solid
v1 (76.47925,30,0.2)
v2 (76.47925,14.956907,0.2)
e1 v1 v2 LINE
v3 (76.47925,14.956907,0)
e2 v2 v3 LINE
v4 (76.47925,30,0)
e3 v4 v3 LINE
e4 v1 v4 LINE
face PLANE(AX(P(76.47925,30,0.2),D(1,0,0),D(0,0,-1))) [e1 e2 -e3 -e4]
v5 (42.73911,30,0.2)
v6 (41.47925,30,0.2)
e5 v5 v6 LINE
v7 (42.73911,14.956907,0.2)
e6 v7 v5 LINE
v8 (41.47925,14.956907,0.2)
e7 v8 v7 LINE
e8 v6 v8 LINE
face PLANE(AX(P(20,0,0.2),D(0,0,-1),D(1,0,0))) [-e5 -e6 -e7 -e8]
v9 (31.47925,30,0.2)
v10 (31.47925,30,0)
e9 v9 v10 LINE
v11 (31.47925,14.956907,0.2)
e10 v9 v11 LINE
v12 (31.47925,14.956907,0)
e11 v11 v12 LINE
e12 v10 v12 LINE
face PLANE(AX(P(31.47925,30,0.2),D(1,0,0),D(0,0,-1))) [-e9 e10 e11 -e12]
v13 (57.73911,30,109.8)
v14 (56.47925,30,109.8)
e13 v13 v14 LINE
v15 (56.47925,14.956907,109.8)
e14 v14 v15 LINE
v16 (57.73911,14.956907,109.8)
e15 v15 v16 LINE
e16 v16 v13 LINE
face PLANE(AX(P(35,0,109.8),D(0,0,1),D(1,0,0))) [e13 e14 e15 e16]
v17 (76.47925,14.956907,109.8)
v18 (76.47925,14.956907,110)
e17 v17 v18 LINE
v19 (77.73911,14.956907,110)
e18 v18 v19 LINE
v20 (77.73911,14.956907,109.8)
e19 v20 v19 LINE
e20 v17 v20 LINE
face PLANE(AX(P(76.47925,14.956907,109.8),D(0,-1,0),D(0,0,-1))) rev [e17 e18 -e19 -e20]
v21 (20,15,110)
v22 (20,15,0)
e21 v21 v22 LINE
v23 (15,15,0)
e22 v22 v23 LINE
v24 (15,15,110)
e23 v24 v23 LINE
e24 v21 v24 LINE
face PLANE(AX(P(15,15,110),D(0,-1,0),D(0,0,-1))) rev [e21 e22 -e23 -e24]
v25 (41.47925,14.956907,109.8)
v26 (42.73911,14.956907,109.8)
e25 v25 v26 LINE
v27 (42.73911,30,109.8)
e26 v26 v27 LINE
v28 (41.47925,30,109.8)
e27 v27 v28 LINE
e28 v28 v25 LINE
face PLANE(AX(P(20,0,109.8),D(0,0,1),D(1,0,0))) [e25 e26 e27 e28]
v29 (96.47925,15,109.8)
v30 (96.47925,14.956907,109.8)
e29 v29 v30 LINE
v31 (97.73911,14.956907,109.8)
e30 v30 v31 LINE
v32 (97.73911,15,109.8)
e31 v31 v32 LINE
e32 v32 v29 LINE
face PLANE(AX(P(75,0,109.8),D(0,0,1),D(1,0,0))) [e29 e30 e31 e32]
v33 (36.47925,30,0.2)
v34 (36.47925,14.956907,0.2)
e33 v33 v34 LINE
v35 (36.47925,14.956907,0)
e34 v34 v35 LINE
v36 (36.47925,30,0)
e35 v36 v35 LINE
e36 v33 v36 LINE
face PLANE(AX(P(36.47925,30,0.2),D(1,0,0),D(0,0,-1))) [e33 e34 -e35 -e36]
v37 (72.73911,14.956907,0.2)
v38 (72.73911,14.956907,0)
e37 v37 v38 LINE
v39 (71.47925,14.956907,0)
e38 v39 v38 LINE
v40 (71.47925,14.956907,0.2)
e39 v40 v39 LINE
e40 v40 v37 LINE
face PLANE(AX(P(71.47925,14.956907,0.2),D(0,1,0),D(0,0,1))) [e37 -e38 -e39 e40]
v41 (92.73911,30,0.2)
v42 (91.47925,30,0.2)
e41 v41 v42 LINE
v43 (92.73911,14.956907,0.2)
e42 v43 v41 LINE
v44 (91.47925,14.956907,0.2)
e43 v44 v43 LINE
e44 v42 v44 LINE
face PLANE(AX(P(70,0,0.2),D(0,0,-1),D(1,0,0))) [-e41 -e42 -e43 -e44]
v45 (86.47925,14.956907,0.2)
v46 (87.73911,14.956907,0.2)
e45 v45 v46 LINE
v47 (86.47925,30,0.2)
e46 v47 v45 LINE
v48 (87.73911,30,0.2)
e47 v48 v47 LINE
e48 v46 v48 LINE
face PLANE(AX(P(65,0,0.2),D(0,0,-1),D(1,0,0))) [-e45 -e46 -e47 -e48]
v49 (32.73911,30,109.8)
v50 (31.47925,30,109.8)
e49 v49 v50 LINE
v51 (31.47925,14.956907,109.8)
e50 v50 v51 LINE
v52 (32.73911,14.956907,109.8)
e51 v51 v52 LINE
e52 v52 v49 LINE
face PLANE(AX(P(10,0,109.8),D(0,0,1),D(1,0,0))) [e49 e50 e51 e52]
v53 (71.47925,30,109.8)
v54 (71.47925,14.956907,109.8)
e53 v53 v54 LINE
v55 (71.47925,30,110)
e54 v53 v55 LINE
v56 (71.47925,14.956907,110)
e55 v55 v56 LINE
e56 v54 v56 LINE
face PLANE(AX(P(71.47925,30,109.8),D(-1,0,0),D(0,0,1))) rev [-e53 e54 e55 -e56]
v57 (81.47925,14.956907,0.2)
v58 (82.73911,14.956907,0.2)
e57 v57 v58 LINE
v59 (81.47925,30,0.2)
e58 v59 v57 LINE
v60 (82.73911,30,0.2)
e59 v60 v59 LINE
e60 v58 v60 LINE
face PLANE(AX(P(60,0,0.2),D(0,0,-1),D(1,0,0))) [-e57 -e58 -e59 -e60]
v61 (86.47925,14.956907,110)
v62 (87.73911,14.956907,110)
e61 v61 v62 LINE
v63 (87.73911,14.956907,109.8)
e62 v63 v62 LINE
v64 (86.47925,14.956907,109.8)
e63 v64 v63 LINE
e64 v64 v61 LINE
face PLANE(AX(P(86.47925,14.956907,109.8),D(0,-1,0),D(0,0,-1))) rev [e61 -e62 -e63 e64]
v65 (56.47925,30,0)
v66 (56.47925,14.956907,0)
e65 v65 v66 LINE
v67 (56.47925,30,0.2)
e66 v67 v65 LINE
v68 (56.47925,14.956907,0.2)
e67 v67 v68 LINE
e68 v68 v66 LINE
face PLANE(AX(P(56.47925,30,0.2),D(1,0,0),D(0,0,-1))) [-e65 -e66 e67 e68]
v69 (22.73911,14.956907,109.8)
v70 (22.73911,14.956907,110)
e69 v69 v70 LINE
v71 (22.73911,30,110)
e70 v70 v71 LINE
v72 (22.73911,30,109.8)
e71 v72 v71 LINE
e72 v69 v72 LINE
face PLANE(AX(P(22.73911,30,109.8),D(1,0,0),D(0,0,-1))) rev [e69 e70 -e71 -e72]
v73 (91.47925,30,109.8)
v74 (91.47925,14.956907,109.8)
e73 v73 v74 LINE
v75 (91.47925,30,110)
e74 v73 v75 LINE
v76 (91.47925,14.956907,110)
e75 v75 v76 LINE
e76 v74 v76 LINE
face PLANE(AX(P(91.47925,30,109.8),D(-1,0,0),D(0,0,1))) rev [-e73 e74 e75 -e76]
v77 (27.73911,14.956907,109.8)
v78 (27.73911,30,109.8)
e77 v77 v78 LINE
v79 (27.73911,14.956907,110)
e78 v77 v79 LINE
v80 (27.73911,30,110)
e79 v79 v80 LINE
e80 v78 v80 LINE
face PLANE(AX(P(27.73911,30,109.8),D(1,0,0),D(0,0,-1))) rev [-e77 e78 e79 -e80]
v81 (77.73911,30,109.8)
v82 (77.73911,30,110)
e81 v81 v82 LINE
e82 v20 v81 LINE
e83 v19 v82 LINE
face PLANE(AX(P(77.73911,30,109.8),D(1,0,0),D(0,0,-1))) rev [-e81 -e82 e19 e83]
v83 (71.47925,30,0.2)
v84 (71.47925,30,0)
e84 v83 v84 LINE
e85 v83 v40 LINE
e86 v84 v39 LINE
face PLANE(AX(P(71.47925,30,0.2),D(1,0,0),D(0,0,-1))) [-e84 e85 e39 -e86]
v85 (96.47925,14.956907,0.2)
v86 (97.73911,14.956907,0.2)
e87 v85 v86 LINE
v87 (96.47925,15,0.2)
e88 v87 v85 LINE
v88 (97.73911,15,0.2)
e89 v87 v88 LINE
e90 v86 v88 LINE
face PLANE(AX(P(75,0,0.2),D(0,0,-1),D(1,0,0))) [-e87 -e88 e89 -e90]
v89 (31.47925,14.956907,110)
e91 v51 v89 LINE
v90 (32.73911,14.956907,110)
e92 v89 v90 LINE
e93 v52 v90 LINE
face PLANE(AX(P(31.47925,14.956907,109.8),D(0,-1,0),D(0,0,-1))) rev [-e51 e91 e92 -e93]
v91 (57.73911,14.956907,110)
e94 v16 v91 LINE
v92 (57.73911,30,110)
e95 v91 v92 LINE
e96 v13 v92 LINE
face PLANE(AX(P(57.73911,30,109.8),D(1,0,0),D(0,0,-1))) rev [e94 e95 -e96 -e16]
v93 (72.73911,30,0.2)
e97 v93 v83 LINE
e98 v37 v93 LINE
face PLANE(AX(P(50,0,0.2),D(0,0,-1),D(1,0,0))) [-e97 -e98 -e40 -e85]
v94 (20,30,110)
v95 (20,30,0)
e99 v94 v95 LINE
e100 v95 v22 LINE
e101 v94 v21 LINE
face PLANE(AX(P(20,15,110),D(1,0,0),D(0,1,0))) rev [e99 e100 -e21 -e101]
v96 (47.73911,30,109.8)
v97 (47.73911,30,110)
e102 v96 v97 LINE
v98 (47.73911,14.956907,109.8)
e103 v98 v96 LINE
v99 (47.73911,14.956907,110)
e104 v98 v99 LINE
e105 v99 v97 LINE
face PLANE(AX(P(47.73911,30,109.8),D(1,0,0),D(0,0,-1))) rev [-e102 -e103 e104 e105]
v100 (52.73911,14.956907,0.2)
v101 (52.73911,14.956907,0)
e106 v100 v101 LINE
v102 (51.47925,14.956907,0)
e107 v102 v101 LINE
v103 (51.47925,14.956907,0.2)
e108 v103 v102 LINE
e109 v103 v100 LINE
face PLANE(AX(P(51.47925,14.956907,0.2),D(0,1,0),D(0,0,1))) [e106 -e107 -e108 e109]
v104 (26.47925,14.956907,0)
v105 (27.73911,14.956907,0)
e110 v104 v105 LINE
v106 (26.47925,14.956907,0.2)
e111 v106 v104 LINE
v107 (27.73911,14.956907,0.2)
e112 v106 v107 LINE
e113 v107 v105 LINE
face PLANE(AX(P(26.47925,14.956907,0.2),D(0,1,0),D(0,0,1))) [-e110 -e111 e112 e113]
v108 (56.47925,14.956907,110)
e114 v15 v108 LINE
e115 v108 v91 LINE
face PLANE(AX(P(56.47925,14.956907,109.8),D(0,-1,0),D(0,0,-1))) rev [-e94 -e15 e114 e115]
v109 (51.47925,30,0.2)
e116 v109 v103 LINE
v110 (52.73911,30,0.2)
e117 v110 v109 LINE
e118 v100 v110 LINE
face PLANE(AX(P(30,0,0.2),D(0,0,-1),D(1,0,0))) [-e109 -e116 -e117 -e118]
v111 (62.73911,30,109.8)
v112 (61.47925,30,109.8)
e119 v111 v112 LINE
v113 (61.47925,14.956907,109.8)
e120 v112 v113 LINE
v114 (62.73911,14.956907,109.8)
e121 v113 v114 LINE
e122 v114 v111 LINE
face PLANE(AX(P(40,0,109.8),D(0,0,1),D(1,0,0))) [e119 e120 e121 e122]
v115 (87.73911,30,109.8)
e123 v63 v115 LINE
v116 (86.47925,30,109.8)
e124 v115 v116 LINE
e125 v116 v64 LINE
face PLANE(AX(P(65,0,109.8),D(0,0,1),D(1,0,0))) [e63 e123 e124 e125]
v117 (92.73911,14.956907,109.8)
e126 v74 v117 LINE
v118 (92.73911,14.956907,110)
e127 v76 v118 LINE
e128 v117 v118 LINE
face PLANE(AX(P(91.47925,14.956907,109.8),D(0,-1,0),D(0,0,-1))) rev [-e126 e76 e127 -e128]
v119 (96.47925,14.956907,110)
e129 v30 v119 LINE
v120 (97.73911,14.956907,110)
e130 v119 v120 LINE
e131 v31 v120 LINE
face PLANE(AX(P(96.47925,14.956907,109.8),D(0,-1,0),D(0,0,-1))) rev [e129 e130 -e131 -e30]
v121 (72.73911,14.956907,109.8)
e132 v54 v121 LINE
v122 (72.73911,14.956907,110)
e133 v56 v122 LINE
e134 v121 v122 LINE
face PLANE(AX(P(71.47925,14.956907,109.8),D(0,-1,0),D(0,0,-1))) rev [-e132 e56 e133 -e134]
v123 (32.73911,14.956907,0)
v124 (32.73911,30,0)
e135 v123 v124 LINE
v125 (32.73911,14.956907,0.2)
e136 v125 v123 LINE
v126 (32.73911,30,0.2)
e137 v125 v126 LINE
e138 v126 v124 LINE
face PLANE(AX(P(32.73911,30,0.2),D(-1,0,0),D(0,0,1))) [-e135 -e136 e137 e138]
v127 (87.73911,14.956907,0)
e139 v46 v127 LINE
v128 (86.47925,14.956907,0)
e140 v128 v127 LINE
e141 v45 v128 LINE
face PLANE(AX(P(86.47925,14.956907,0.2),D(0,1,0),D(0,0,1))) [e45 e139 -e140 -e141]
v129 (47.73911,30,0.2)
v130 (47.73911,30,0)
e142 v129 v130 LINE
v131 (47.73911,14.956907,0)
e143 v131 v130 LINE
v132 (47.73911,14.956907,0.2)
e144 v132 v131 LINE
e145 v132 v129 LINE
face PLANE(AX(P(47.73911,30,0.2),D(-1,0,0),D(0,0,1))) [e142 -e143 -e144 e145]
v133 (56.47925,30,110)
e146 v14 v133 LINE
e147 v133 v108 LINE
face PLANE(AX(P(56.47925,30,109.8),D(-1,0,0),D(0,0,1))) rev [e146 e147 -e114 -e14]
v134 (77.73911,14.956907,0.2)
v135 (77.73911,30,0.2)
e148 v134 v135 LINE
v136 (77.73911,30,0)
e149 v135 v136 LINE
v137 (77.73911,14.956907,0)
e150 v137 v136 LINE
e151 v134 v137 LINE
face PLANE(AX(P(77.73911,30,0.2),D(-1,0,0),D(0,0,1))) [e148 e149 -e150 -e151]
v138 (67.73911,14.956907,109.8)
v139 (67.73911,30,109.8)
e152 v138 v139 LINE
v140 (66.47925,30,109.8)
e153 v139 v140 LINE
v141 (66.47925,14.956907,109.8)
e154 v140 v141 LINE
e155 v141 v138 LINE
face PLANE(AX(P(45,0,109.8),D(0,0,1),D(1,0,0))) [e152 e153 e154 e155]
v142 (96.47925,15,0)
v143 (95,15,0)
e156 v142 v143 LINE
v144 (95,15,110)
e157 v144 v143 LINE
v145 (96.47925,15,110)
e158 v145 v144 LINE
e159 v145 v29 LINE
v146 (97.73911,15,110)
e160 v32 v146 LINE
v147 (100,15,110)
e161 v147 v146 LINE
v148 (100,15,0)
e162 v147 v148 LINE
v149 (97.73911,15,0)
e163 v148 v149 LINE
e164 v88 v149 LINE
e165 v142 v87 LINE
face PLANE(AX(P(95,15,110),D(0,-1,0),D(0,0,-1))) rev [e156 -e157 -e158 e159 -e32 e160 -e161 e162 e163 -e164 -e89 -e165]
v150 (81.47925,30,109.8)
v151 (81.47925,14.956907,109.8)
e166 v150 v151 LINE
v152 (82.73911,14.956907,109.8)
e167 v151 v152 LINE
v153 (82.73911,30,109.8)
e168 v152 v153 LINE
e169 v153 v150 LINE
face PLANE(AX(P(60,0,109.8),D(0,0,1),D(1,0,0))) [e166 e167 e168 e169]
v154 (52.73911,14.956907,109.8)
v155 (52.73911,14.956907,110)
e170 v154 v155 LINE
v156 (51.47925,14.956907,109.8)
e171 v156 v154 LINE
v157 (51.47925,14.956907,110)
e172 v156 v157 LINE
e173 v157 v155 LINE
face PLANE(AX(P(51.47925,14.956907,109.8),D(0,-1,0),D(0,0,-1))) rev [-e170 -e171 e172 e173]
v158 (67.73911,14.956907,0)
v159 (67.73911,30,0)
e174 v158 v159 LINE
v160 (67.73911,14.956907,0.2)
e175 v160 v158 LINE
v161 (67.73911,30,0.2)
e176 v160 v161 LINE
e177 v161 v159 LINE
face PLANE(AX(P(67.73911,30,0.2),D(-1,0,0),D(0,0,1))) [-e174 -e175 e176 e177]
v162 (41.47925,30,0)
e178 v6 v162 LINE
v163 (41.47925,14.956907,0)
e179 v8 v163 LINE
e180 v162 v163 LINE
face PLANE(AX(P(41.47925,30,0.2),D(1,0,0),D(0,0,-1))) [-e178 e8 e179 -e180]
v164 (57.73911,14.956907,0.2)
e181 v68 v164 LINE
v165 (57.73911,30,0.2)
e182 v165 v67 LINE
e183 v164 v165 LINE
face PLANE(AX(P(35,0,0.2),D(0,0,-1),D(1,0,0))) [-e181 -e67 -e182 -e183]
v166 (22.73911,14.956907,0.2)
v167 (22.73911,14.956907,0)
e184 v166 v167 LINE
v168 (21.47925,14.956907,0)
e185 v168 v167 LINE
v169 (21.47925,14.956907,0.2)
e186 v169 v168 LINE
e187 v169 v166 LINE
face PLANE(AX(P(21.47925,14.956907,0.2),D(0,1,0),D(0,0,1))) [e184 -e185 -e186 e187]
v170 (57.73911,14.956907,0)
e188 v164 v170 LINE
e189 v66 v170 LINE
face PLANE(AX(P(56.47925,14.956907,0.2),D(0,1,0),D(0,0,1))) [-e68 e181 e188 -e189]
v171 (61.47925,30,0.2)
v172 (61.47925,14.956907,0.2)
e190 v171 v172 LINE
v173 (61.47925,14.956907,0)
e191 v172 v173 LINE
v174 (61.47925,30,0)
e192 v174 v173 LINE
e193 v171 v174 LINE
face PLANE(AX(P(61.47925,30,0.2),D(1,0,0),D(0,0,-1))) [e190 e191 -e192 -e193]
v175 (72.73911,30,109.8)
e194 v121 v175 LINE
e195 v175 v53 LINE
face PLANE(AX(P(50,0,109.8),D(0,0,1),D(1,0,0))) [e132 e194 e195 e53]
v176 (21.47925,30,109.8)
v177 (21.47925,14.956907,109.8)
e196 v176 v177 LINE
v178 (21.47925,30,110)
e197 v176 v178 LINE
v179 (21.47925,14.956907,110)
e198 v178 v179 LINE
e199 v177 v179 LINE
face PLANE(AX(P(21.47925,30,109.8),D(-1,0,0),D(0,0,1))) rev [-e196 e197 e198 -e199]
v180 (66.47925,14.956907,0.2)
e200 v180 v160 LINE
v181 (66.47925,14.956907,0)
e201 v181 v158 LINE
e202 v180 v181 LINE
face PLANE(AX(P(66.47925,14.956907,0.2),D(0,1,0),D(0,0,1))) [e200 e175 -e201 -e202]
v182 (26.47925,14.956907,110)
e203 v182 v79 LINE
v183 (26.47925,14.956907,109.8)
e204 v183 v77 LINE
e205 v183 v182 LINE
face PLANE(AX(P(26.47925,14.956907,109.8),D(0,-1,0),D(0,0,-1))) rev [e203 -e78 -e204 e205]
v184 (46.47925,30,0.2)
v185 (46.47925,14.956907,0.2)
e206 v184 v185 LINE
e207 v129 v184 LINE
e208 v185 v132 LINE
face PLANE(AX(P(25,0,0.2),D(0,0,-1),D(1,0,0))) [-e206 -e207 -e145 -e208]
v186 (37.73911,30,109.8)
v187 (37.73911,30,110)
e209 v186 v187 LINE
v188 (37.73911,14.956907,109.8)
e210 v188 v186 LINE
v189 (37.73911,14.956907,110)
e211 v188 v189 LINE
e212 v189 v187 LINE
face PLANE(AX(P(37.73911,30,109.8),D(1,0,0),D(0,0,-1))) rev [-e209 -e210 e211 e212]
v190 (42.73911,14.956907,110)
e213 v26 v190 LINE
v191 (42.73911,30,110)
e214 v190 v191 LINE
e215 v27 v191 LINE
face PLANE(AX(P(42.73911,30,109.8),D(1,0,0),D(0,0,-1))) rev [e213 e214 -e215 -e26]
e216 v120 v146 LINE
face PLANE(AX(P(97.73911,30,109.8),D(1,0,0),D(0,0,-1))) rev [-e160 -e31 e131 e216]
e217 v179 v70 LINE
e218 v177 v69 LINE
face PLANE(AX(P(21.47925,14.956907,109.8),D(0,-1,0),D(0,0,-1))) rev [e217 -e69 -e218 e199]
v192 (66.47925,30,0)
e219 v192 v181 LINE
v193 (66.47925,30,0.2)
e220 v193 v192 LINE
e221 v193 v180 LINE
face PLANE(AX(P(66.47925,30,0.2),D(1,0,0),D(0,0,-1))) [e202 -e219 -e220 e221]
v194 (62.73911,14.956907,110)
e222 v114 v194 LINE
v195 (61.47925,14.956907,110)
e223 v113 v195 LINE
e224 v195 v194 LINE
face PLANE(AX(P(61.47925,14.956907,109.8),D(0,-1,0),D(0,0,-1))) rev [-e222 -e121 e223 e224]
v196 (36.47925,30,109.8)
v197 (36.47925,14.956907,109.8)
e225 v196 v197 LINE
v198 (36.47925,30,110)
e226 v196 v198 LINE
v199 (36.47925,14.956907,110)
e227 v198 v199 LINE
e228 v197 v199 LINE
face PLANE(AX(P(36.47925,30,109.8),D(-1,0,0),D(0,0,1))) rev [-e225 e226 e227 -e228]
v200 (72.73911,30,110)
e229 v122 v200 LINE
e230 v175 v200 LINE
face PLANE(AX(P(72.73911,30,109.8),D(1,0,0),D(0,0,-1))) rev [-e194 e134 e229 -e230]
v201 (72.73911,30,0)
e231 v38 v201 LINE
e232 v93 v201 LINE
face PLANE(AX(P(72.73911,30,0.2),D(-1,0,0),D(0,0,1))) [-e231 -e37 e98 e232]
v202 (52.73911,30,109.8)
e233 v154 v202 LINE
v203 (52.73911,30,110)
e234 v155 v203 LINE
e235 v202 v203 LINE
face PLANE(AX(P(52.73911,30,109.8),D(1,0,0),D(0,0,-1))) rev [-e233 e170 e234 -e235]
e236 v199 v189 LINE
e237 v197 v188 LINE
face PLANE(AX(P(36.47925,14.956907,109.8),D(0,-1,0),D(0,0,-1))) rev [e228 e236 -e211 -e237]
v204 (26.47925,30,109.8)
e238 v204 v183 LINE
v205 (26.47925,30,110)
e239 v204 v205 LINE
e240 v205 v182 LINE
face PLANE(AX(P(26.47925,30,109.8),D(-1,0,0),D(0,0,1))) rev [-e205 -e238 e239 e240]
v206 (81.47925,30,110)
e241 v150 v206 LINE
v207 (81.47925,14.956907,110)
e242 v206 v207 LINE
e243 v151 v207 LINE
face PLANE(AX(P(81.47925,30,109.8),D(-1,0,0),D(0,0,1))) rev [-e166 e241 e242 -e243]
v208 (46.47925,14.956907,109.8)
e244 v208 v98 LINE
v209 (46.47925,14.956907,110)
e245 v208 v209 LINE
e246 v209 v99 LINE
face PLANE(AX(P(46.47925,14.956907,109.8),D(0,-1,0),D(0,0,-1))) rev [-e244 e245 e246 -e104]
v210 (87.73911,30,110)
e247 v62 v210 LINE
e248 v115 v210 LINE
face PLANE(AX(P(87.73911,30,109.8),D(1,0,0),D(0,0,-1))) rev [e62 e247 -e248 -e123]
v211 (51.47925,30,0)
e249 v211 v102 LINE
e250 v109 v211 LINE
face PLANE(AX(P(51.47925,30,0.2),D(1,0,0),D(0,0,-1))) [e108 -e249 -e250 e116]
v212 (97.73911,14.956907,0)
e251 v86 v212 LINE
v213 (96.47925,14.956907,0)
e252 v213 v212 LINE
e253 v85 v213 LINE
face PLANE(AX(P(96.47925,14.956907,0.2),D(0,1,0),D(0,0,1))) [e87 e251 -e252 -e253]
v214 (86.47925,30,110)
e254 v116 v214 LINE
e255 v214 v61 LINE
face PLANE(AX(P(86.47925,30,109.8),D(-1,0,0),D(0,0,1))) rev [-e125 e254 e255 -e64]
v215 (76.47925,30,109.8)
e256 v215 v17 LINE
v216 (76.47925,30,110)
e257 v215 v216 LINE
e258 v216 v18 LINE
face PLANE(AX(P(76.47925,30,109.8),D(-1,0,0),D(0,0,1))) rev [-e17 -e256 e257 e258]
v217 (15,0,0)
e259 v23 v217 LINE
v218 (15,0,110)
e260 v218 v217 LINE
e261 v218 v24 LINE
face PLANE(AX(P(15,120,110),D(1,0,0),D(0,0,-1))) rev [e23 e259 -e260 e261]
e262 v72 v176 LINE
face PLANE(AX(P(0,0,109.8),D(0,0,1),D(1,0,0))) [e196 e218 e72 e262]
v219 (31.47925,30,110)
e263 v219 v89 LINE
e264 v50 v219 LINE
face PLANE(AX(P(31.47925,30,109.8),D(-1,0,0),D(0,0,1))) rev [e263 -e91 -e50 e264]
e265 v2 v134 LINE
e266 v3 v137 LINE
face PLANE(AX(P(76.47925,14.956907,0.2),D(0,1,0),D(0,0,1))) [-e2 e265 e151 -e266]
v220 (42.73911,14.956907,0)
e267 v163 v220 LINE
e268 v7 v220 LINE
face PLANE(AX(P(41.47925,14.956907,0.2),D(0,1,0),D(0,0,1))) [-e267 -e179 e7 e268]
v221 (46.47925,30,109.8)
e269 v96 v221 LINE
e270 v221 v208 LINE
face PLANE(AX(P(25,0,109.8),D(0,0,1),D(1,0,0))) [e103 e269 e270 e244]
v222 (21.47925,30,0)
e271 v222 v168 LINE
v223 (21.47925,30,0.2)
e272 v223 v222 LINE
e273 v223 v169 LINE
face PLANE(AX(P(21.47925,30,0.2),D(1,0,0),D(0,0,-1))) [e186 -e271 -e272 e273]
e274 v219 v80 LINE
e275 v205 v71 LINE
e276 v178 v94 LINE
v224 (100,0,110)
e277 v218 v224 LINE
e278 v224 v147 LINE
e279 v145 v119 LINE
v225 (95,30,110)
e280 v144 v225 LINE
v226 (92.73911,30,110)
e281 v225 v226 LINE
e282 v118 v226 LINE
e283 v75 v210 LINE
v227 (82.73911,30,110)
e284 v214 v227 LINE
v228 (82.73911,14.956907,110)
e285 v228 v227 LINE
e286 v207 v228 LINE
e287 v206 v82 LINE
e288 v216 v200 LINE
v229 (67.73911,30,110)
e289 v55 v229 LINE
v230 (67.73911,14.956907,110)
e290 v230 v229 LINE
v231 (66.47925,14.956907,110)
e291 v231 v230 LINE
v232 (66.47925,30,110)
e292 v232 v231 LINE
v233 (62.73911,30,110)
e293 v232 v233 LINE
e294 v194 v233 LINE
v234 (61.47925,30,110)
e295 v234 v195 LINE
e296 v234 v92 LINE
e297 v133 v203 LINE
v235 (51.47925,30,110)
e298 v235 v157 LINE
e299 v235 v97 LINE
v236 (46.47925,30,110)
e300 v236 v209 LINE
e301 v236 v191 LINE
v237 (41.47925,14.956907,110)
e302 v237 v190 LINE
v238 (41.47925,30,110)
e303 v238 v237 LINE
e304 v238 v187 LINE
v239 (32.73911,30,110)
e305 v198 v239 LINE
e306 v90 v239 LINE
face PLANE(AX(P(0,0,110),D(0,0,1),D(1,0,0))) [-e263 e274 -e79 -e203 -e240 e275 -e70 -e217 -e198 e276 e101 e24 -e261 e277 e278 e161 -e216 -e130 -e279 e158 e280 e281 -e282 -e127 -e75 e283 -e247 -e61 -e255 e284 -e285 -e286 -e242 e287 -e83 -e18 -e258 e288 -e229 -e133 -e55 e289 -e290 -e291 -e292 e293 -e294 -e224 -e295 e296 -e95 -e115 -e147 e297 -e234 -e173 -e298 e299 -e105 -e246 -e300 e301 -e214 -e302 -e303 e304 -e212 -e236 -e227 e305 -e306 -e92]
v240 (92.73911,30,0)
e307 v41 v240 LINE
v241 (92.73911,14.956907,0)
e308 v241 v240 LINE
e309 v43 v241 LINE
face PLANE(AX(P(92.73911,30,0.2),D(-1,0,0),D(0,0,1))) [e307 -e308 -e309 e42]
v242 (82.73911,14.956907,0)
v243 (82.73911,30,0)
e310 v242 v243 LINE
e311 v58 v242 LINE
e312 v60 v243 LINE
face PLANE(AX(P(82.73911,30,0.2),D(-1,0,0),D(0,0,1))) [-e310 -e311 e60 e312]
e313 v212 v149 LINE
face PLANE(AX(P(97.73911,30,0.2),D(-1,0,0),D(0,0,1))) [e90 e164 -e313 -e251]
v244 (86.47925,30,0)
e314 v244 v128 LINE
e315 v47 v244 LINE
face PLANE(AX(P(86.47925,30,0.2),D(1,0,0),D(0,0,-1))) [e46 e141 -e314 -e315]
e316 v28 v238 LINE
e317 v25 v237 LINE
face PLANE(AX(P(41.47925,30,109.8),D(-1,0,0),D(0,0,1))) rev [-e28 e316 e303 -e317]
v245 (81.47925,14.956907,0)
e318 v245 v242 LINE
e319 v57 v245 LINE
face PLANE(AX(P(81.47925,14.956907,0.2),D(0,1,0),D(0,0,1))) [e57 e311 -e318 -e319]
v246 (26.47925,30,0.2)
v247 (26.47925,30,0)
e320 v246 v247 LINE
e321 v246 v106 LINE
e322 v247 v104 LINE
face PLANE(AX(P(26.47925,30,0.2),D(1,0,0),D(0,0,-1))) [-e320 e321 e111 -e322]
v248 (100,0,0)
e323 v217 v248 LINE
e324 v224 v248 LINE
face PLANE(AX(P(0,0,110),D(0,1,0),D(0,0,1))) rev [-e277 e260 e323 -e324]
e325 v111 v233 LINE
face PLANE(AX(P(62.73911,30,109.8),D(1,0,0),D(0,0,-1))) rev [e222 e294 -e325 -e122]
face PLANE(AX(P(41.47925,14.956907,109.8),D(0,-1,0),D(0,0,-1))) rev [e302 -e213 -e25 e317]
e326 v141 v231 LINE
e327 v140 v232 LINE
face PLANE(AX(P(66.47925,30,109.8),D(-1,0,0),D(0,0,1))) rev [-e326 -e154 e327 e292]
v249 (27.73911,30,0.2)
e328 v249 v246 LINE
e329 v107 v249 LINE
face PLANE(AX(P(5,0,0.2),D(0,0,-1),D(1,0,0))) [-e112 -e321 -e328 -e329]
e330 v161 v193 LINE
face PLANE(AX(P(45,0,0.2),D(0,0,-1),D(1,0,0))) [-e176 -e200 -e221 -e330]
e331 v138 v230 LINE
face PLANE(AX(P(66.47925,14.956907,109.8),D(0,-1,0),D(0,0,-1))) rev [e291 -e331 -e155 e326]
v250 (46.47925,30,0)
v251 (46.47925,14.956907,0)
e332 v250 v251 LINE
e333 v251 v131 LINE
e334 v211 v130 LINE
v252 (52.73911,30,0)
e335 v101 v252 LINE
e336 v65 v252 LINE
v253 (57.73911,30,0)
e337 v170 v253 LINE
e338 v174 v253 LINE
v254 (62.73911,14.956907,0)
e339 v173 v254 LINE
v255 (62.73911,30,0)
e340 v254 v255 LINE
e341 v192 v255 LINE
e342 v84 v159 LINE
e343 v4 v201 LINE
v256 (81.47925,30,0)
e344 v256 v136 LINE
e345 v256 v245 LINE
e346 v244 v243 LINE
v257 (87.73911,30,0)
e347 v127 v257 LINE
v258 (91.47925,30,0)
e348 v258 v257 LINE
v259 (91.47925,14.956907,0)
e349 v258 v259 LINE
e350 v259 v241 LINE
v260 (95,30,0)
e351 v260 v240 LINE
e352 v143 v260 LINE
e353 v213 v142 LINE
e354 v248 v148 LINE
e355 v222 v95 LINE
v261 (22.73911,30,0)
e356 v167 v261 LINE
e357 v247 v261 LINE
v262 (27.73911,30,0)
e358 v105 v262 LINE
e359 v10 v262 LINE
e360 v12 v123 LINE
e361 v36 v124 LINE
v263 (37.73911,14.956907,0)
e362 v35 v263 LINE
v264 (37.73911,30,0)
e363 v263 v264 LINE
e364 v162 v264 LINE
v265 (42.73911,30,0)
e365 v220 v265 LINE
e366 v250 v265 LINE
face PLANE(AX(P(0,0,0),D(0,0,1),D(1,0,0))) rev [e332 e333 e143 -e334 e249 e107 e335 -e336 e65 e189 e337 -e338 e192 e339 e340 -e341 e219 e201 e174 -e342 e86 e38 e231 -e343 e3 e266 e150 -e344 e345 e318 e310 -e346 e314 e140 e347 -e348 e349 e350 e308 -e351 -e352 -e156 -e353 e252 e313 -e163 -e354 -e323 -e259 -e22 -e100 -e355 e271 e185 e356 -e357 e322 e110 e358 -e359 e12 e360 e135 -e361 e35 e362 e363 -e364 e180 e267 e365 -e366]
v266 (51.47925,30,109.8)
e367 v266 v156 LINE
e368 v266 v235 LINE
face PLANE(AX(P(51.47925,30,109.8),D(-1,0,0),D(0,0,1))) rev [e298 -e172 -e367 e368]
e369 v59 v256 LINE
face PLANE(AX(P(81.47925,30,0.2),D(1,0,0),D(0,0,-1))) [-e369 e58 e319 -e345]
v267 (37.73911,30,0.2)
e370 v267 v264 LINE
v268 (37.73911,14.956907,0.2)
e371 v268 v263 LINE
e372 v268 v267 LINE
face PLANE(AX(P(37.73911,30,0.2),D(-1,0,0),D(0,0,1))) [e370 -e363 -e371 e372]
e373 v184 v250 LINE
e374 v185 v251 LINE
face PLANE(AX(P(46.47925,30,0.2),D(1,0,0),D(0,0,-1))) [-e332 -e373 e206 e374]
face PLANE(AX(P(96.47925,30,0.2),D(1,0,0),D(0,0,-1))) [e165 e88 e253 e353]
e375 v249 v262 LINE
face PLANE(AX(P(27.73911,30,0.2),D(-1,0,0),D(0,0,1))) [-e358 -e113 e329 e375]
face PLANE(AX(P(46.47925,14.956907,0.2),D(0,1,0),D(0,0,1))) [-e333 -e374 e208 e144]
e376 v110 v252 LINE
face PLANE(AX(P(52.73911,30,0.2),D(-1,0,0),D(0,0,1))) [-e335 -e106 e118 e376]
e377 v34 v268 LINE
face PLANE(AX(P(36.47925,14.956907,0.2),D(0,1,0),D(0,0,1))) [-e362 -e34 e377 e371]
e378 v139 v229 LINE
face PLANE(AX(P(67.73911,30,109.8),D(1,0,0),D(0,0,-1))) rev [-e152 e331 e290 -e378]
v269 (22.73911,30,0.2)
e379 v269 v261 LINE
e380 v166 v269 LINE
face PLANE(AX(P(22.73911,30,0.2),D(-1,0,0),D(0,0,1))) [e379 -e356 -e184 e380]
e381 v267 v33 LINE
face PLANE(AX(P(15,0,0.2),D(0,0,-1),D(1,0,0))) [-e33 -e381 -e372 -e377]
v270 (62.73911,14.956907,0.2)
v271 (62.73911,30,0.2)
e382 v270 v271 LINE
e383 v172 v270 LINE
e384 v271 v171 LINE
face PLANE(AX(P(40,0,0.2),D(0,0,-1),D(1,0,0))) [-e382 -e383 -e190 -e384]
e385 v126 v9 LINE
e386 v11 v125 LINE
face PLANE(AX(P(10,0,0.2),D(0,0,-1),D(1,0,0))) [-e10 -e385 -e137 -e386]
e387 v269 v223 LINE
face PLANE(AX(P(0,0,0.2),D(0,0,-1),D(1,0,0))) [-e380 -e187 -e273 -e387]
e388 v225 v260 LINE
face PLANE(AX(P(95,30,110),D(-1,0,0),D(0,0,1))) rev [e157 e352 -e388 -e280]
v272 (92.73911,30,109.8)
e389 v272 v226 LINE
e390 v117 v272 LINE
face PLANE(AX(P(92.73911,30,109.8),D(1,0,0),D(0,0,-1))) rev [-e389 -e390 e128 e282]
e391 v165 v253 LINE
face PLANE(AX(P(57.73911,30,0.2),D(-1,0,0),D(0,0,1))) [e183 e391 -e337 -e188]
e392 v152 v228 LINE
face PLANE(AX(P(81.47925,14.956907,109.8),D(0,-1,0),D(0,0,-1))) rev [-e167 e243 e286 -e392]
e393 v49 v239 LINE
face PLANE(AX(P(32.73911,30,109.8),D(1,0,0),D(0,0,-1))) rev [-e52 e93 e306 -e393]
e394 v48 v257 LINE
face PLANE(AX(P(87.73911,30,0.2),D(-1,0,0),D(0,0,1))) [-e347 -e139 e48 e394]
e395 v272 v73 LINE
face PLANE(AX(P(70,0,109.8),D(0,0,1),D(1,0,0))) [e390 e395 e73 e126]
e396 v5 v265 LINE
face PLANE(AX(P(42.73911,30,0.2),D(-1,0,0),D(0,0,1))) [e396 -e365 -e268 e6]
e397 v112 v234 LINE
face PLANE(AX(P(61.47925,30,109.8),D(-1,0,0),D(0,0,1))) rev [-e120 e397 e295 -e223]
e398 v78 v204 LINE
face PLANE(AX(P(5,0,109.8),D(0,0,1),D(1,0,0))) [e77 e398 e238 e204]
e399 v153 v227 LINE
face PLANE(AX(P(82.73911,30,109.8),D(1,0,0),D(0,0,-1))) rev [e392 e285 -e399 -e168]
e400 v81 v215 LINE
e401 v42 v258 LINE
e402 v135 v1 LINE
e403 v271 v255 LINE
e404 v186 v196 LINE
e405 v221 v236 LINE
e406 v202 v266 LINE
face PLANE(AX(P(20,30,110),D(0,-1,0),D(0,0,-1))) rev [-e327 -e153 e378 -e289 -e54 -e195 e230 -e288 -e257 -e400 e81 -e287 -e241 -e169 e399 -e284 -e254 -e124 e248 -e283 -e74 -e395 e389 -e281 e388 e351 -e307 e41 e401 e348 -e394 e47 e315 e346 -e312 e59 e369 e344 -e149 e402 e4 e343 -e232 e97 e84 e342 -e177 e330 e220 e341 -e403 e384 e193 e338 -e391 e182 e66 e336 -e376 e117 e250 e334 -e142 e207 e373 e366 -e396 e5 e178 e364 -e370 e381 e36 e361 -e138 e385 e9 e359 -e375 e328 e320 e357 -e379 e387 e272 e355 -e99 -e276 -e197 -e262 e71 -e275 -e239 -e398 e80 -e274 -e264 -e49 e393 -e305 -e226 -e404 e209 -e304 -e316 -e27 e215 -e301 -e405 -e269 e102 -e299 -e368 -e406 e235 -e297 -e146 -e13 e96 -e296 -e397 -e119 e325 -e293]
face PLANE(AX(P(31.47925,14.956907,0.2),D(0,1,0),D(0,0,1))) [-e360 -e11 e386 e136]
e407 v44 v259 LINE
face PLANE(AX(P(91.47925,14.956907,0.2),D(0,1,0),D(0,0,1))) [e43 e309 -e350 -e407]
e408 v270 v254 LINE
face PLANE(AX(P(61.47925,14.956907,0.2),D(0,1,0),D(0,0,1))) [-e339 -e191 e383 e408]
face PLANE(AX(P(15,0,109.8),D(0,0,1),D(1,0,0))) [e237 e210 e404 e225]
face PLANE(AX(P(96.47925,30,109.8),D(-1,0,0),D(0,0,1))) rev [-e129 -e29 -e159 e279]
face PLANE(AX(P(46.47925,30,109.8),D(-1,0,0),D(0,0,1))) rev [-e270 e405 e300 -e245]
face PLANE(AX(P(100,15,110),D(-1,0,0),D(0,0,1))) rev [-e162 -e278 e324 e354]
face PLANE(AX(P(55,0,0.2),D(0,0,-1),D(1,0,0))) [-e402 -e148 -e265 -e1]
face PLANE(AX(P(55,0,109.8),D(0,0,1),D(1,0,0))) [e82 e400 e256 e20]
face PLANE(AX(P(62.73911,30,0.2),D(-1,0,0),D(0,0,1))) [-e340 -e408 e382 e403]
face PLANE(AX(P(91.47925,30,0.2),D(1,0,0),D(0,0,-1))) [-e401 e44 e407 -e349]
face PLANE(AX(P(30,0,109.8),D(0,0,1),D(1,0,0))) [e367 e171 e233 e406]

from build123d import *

# Parameters (mm, degrees)
BOSS_EXTRUDE1_DEPTH      = 110
SKETCH2_W                = 1.259860676
SKETCH2_H                = 15.043092937
CUT_EXTRUDE1_DEPTH       = 0.2
LPATTERN1_COUNT          = 16
LPATTERN1_PITCH          = 5
MIRROR1_COPY_1_SKETCH_W  = 1.259860676
MIRROR1_COPY_1_SKETCH_H  = 15.043092937
MIRROR1_COPY_1_DEPTH     = 0.2
MIRROR1_COPY_2_SKETCH_W  = 1.259860676
MIRROR1_COPY_2_SKETCH_H  = 15.043092937
MIRROR1_COPY_2_DEPTH     = 0.2
MIRROR1_COPY_3_SKETCH_W  = 1.259860676
MIRROR1_COPY_3_SKETCH_H  = 15.043092937
MIRROR1_COPY_3_DEPTH     = 0.2
MIRROR1_COPY_4_SKETCH_W  = 1.259860676
MIRROR1_COPY_4_SKETCH_H  = 15.043092937
MIRROR1_COPY_4_DEPTH     = 0.2
MIRROR1_COPY_5_SKETCH_W  = 1.259860676
MIRROR1_COPY_5_SKETCH_H  = 15.043092937
MIRROR1_COPY_5_DEPTH     = 0.2
MIRROR1_COPY_6_SKETCH_W  = 1.259860676
MIRROR1_COPY_6_SKETCH_H  = 15.043092937
MIRROR1_COPY_6_DEPTH     = 0.2
MIRROR1_COPY_7_SKETCH_W  = 1.259860676
MIRROR1_COPY_7_SKETCH_H  = 15.043092937
MIRROR1_COPY_7_DEPTH     = 0.2
MIRROR1_COPY_8_SKETCH_W  = 1.259860676
MIRROR1_COPY_8_SKETCH_H  = 15.043092937
MIRROR1_COPY_8_DEPTH     = 0.2
MIRROR1_COPY_9_SKETCH_W  = 1.259860676
MIRROR1_COPY_9_SKETCH_H  = 15.043092937
MIRROR1_COPY_9_DEPTH     = 0.2
MIRROR1_COPY_10_SKETCH_W = 1.259860676
MIRROR1_COPY_10_SKETCH_H = 15.043092937
MIRROR1_COPY_10_DEPTH    = 0.2
MIRROR1_COPY_11_SKETCH_W = 1.259860676
MIRROR1_COPY_11_SKETCH_H = 15.043092937
MIRROR1_COPY_11_DEPTH    = 0.2
MIRROR1_COPY_12_SKETCH_W = 1.259860676
MIRROR1_COPY_12_SKETCH_H = 15.043092937
MIRROR1_COPY_12_DEPTH    = 0.2
MIRROR1_COPY_13_SKETCH_W = 1.259860676
MIRROR1_COPY_13_SKETCH_H = 15.043092937
MIRROR1_COPY_13_DEPTH    = 0.2
MIRROR1_COPY_14_SKETCH_W = 1.259860676
MIRROR1_COPY_14_SKETCH_H = 15.043092937
MIRROR1_COPY_14_DEPTH    = 0.2
MIRROR1_COPY_15_SKETCH_W = 1.259860676
MIRROR1_COPY_15_SKETCH_H = 15.043092937
MIRROR1_COPY_15_DEPTH    = 0.2
SKETCH4_W                = 38.958676741
SKETCH4_H                = 137.401414086
CUT_EXTRUDE2_DEPTH       = 192.049731745


with BuildPart() as part:
    # Sketch1 → Boss-Extrude1 (new body)
    with BuildSketch(Plane.XY):
        Polygon((0, 0), (100, 0), (100, 15), (95, 15), (95, 30), (20, 30), (20, 15), (15, 15), (15, 120), (0, 120), align=None)
    extrude(amount=BOSS_EXTRUDE1_DEPTH)

    # Sketch2 → Cut-Extrude1 (cut)
    with BuildSketch(Plane.XY.offset(110)):
        with Locations((22.109179897, 22.478453532)):
            Rectangle(SKETCH2_W, SKETCH2_H)
    cut_extrude1 = extrude(amount=-CUT_EXTRUDE1_DEPTH, mode=Mode.SUBTRACT)

    # LPattern1: Cut-Extrude1 ×16
    with Locations(*[(i * LPATTERN1_PITCH, 0, 0) for i in range(1, LPATTERN1_COUNT)]):
        add(cut_extrude1, mode=Mode.SUBTRACT)

    # Mirror1: Cut-Extrude1 across plane
    add(cut_extrude1.mirror(Plane(origin=(0, 0, 55), x_dir=(1, 0, 0), z_dir=(0, 0, -1))), mode=Mode.SUBTRACT)

    # Mirror1 copy 1 sketch → Mirror1 copy 1 (cut)
    with BuildSketch(Plane(origin=(5, 0, 0), x_dir=(1, 0, 0), z_dir=(0, 0, -1))):
        with Locations((22.109179897, -22.478453532)):
            Rectangle(MIRROR1_COPY_1_SKETCH_W, MIRROR1_COPY_1_SKETCH_H)
    extrude(amount=-MIRROR1_COPY_1_DEPTH, mode=Mode.SUBTRACT)

    # Mirror1 copy 2 sketch → Mirror1 copy 2 (cut)
    with BuildSketch(Plane(origin=(10, 0, 0), x_dir=(1, 0, 0), z_dir=(0, 0, -1))):
        with Locations((22.109179897, -22.478453532)):
            Rectangle(MIRROR1_COPY_2_SKETCH_W, MIRROR1_COPY_2_SKETCH_H)
    extrude(amount=-MIRROR1_COPY_2_DEPTH, mode=Mode.SUBTRACT)

    # Mirror1 copy 3 sketch → Mirror1 copy 3 (cut)
    with BuildSketch(Plane(origin=(15, 0, 0), x_dir=(1, 0, 0), z_dir=(0, 0, -1))):
        with Locations((22.109179897, -22.478453532)):
            Rectangle(MIRROR1_COPY_3_SKETCH_W, MIRROR1_COPY_3_SKETCH_H)
    extrude(amount=-MIRROR1_COPY_3_DEPTH, mode=Mode.SUBTRACT)

    # Mirror1 copy 4 sketch → Mirror1 copy 4 (cut)
    with BuildSketch(Plane(origin=(20, 0, 0), x_dir=(1, 0, 0), z_dir=(0, 0, -1))):
        with Locations((22.109179897, -22.478453532)):
            Rectangle(MIRROR1_COPY_4_SKETCH_W, MIRROR1_COPY_4_SKETCH_H)
    extrude(amount=-MIRROR1_COPY_4_DEPTH, mode=Mode.SUBTRACT)

    # Mirror1 copy 5 sketch → Mirror1 copy 5 (cut)
    with BuildSketch(Plane(origin=(25, 0, 0), x_dir=(1, 0, 0), z_dir=(0, 0, -1))):
        with Locations((22.109179897, -22.478453532)):
            Rectangle(MIRROR1_COPY_5_SKETCH_W, MIRROR1_COPY_5_SKETCH_H)
    extrude(amount=-MIRROR1_COPY_5_DEPTH, mode=Mode.SUBTRACT)

    # Mirror1 copy 6 sketch → Mirror1 copy 6 (cut)
    with BuildSketch(Plane(origin=(30, 0, 0), x_dir=(1, 0, 0), z_dir=(0, 0, -1))):
        with Locations((22.109179897, -22.478453532)):
            Rectangle(MIRROR1_COPY_6_SKETCH_W, MIRROR1_COPY_6_SKETCH_H)
    extrude(amount=-MIRROR1_COPY_6_DEPTH, mode=Mode.SUBTRACT)

    # Mirror1 copy 7 sketch → Mirror1 copy 7 (cut)
    with BuildSketch(Plane(origin=(35, 0, 0), x_dir=(1, 0, 0), z_dir=(0, 0, -1))):
        with Locations((22.109179897, -22.478453532)):
            Rectangle(MIRROR1_COPY_7_SKETCH_W, MIRROR1_COPY_7_SKETCH_H)
    extrude(amount=-MIRROR1_COPY_7_DEPTH, mode=Mode.SUBTRACT)

    # Mirror1 copy 8 sketch → Mirror1 copy 8 (cut)
    with BuildSketch(Plane(origin=(40, 0, 0), x_dir=(1, 0, 0), z_dir=(0, 0, -1))):
        with Locations((22.109179897, -22.478453532)):
            Rectangle(MIRROR1_COPY_8_SKETCH_W, MIRROR1_COPY_8_SKETCH_H)
    extrude(amount=-MIRROR1_COPY_8_DEPTH, mode=Mode.SUBTRACT)

    # Mirror1 copy 9 sketch → Mirror1 copy 9 (cut)
    with BuildSketch(Plane(origin=(45, 0, 0), x_dir=(1, 0, 0), z_dir=(0, 0, -1))):
        with Locations((22.109179897, -22.478453532)):
            Rectangle(MIRROR1_COPY_9_SKETCH_W, MIRROR1_COPY_9_SKETCH_H)
    extrude(amount=-MIRROR1_COPY_9_DEPTH, mode=Mode.SUBTRACT)

    # Mirror1 copy 10 sketch → Mirror1 copy 10 (cut)
    with BuildSketch(Plane(origin=(50, 0, 0), x_dir=(1, 0, 0), z_dir=(0, 0, -1))):
        with Locations((22.109179897, -22.478453532)):
            Rectangle(MIRROR1_COPY_10_SKETCH_W, MIRROR1_COPY_10_SKETCH_H)
    extrude(amount=-MIRROR1_COPY_10_DEPTH, mode=Mode.SUBTRACT)

    # Mirror1 copy 11 sketch → Mirror1 copy 11 (cut)
    with BuildSketch(Plane(origin=(55, 0, 0), x_dir=(1, 0, 0), z_dir=(0, 0, -1))):
        with Locations((22.109179897, -22.478453532)):
            Rectangle(MIRROR1_COPY_11_SKETCH_W, MIRROR1_COPY_11_SKETCH_H)
    extrude(amount=-MIRROR1_COPY_11_DEPTH, mode=Mode.SUBTRACT)

    # Mirror1 copy 12 sketch → Mirror1 copy 12 (cut)
    with BuildSketch(Plane(origin=(60, 0, 0), x_dir=(1, 0, 0), z_dir=(0, 0, -1))):
        with Locations((22.109179897, -22.478453532)):
            Rectangle(MIRROR1_COPY_12_SKETCH_W, MIRROR1_COPY_12_SKETCH_H)
    extrude(amount=-MIRROR1_COPY_12_DEPTH, mode=Mode.SUBTRACT)

    # Mirror1 copy 13 sketch → Mirror1 copy 13 (cut)
    with BuildSketch(Plane(origin=(65, 0, 0), x_dir=(1, 0, 0), z_dir=(0, 0, -1))):
        with Locations((22.109179897, -22.478453532)):
            Rectangle(MIRROR1_COPY_13_SKETCH_W, MIRROR1_COPY_13_SKETCH_H)
    extrude(amount=-MIRROR1_COPY_13_DEPTH, mode=Mode.SUBTRACT)

    # Mirror1 copy 14 sketch → Mirror1 copy 14 (cut)
    with BuildSketch(Plane(origin=(70, 0, 0), x_dir=(1, 0, 0), z_dir=(0, 0, -1))):
        with Locations((22.109179897, -22.478453532)):
            Rectangle(MIRROR1_COPY_14_SKETCH_W, MIRROR1_COPY_14_SKETCH_H)
    extrude(amount=-MIRROR1_COPY_14_DEPTH, mode=Mode.SUBTRACT)

    # Mirror1 copy 15 sketch → Mirror1 copy 15 (cut)
    with BuildSketch(Plane(origin=(75, 0, 0), x_dir=(1, 0, 0), z_dir=(0, 0, -1))):
        with Locations((22.109179897, -22.478453532)):
            Rectangle(MIRROR1_COPY_15_SKETCH_W, MIRROR1_COPY_15_SKETCH_H)
    extrude(amount=-MIRROR1_COPY_15_DEPTH, mode=Mode.SUBTRACT)

    # Sketch4 → Cut-Extrude2 (cut, through all)
    with BuildSketch(Plane(origin=(0, 0, 0), x_dir=(-1, 0, 0), z_dir=(0, 0, -1))):
        with Locations((4.47933837, 51.299292957)):
            Rectangle(SKETCH4_W, SKETCH4_H)
    extrude(amount=-CUT_EXTRUDE2_DEPTH, mode=Mode.SUBTRACT)


solid = part.part
